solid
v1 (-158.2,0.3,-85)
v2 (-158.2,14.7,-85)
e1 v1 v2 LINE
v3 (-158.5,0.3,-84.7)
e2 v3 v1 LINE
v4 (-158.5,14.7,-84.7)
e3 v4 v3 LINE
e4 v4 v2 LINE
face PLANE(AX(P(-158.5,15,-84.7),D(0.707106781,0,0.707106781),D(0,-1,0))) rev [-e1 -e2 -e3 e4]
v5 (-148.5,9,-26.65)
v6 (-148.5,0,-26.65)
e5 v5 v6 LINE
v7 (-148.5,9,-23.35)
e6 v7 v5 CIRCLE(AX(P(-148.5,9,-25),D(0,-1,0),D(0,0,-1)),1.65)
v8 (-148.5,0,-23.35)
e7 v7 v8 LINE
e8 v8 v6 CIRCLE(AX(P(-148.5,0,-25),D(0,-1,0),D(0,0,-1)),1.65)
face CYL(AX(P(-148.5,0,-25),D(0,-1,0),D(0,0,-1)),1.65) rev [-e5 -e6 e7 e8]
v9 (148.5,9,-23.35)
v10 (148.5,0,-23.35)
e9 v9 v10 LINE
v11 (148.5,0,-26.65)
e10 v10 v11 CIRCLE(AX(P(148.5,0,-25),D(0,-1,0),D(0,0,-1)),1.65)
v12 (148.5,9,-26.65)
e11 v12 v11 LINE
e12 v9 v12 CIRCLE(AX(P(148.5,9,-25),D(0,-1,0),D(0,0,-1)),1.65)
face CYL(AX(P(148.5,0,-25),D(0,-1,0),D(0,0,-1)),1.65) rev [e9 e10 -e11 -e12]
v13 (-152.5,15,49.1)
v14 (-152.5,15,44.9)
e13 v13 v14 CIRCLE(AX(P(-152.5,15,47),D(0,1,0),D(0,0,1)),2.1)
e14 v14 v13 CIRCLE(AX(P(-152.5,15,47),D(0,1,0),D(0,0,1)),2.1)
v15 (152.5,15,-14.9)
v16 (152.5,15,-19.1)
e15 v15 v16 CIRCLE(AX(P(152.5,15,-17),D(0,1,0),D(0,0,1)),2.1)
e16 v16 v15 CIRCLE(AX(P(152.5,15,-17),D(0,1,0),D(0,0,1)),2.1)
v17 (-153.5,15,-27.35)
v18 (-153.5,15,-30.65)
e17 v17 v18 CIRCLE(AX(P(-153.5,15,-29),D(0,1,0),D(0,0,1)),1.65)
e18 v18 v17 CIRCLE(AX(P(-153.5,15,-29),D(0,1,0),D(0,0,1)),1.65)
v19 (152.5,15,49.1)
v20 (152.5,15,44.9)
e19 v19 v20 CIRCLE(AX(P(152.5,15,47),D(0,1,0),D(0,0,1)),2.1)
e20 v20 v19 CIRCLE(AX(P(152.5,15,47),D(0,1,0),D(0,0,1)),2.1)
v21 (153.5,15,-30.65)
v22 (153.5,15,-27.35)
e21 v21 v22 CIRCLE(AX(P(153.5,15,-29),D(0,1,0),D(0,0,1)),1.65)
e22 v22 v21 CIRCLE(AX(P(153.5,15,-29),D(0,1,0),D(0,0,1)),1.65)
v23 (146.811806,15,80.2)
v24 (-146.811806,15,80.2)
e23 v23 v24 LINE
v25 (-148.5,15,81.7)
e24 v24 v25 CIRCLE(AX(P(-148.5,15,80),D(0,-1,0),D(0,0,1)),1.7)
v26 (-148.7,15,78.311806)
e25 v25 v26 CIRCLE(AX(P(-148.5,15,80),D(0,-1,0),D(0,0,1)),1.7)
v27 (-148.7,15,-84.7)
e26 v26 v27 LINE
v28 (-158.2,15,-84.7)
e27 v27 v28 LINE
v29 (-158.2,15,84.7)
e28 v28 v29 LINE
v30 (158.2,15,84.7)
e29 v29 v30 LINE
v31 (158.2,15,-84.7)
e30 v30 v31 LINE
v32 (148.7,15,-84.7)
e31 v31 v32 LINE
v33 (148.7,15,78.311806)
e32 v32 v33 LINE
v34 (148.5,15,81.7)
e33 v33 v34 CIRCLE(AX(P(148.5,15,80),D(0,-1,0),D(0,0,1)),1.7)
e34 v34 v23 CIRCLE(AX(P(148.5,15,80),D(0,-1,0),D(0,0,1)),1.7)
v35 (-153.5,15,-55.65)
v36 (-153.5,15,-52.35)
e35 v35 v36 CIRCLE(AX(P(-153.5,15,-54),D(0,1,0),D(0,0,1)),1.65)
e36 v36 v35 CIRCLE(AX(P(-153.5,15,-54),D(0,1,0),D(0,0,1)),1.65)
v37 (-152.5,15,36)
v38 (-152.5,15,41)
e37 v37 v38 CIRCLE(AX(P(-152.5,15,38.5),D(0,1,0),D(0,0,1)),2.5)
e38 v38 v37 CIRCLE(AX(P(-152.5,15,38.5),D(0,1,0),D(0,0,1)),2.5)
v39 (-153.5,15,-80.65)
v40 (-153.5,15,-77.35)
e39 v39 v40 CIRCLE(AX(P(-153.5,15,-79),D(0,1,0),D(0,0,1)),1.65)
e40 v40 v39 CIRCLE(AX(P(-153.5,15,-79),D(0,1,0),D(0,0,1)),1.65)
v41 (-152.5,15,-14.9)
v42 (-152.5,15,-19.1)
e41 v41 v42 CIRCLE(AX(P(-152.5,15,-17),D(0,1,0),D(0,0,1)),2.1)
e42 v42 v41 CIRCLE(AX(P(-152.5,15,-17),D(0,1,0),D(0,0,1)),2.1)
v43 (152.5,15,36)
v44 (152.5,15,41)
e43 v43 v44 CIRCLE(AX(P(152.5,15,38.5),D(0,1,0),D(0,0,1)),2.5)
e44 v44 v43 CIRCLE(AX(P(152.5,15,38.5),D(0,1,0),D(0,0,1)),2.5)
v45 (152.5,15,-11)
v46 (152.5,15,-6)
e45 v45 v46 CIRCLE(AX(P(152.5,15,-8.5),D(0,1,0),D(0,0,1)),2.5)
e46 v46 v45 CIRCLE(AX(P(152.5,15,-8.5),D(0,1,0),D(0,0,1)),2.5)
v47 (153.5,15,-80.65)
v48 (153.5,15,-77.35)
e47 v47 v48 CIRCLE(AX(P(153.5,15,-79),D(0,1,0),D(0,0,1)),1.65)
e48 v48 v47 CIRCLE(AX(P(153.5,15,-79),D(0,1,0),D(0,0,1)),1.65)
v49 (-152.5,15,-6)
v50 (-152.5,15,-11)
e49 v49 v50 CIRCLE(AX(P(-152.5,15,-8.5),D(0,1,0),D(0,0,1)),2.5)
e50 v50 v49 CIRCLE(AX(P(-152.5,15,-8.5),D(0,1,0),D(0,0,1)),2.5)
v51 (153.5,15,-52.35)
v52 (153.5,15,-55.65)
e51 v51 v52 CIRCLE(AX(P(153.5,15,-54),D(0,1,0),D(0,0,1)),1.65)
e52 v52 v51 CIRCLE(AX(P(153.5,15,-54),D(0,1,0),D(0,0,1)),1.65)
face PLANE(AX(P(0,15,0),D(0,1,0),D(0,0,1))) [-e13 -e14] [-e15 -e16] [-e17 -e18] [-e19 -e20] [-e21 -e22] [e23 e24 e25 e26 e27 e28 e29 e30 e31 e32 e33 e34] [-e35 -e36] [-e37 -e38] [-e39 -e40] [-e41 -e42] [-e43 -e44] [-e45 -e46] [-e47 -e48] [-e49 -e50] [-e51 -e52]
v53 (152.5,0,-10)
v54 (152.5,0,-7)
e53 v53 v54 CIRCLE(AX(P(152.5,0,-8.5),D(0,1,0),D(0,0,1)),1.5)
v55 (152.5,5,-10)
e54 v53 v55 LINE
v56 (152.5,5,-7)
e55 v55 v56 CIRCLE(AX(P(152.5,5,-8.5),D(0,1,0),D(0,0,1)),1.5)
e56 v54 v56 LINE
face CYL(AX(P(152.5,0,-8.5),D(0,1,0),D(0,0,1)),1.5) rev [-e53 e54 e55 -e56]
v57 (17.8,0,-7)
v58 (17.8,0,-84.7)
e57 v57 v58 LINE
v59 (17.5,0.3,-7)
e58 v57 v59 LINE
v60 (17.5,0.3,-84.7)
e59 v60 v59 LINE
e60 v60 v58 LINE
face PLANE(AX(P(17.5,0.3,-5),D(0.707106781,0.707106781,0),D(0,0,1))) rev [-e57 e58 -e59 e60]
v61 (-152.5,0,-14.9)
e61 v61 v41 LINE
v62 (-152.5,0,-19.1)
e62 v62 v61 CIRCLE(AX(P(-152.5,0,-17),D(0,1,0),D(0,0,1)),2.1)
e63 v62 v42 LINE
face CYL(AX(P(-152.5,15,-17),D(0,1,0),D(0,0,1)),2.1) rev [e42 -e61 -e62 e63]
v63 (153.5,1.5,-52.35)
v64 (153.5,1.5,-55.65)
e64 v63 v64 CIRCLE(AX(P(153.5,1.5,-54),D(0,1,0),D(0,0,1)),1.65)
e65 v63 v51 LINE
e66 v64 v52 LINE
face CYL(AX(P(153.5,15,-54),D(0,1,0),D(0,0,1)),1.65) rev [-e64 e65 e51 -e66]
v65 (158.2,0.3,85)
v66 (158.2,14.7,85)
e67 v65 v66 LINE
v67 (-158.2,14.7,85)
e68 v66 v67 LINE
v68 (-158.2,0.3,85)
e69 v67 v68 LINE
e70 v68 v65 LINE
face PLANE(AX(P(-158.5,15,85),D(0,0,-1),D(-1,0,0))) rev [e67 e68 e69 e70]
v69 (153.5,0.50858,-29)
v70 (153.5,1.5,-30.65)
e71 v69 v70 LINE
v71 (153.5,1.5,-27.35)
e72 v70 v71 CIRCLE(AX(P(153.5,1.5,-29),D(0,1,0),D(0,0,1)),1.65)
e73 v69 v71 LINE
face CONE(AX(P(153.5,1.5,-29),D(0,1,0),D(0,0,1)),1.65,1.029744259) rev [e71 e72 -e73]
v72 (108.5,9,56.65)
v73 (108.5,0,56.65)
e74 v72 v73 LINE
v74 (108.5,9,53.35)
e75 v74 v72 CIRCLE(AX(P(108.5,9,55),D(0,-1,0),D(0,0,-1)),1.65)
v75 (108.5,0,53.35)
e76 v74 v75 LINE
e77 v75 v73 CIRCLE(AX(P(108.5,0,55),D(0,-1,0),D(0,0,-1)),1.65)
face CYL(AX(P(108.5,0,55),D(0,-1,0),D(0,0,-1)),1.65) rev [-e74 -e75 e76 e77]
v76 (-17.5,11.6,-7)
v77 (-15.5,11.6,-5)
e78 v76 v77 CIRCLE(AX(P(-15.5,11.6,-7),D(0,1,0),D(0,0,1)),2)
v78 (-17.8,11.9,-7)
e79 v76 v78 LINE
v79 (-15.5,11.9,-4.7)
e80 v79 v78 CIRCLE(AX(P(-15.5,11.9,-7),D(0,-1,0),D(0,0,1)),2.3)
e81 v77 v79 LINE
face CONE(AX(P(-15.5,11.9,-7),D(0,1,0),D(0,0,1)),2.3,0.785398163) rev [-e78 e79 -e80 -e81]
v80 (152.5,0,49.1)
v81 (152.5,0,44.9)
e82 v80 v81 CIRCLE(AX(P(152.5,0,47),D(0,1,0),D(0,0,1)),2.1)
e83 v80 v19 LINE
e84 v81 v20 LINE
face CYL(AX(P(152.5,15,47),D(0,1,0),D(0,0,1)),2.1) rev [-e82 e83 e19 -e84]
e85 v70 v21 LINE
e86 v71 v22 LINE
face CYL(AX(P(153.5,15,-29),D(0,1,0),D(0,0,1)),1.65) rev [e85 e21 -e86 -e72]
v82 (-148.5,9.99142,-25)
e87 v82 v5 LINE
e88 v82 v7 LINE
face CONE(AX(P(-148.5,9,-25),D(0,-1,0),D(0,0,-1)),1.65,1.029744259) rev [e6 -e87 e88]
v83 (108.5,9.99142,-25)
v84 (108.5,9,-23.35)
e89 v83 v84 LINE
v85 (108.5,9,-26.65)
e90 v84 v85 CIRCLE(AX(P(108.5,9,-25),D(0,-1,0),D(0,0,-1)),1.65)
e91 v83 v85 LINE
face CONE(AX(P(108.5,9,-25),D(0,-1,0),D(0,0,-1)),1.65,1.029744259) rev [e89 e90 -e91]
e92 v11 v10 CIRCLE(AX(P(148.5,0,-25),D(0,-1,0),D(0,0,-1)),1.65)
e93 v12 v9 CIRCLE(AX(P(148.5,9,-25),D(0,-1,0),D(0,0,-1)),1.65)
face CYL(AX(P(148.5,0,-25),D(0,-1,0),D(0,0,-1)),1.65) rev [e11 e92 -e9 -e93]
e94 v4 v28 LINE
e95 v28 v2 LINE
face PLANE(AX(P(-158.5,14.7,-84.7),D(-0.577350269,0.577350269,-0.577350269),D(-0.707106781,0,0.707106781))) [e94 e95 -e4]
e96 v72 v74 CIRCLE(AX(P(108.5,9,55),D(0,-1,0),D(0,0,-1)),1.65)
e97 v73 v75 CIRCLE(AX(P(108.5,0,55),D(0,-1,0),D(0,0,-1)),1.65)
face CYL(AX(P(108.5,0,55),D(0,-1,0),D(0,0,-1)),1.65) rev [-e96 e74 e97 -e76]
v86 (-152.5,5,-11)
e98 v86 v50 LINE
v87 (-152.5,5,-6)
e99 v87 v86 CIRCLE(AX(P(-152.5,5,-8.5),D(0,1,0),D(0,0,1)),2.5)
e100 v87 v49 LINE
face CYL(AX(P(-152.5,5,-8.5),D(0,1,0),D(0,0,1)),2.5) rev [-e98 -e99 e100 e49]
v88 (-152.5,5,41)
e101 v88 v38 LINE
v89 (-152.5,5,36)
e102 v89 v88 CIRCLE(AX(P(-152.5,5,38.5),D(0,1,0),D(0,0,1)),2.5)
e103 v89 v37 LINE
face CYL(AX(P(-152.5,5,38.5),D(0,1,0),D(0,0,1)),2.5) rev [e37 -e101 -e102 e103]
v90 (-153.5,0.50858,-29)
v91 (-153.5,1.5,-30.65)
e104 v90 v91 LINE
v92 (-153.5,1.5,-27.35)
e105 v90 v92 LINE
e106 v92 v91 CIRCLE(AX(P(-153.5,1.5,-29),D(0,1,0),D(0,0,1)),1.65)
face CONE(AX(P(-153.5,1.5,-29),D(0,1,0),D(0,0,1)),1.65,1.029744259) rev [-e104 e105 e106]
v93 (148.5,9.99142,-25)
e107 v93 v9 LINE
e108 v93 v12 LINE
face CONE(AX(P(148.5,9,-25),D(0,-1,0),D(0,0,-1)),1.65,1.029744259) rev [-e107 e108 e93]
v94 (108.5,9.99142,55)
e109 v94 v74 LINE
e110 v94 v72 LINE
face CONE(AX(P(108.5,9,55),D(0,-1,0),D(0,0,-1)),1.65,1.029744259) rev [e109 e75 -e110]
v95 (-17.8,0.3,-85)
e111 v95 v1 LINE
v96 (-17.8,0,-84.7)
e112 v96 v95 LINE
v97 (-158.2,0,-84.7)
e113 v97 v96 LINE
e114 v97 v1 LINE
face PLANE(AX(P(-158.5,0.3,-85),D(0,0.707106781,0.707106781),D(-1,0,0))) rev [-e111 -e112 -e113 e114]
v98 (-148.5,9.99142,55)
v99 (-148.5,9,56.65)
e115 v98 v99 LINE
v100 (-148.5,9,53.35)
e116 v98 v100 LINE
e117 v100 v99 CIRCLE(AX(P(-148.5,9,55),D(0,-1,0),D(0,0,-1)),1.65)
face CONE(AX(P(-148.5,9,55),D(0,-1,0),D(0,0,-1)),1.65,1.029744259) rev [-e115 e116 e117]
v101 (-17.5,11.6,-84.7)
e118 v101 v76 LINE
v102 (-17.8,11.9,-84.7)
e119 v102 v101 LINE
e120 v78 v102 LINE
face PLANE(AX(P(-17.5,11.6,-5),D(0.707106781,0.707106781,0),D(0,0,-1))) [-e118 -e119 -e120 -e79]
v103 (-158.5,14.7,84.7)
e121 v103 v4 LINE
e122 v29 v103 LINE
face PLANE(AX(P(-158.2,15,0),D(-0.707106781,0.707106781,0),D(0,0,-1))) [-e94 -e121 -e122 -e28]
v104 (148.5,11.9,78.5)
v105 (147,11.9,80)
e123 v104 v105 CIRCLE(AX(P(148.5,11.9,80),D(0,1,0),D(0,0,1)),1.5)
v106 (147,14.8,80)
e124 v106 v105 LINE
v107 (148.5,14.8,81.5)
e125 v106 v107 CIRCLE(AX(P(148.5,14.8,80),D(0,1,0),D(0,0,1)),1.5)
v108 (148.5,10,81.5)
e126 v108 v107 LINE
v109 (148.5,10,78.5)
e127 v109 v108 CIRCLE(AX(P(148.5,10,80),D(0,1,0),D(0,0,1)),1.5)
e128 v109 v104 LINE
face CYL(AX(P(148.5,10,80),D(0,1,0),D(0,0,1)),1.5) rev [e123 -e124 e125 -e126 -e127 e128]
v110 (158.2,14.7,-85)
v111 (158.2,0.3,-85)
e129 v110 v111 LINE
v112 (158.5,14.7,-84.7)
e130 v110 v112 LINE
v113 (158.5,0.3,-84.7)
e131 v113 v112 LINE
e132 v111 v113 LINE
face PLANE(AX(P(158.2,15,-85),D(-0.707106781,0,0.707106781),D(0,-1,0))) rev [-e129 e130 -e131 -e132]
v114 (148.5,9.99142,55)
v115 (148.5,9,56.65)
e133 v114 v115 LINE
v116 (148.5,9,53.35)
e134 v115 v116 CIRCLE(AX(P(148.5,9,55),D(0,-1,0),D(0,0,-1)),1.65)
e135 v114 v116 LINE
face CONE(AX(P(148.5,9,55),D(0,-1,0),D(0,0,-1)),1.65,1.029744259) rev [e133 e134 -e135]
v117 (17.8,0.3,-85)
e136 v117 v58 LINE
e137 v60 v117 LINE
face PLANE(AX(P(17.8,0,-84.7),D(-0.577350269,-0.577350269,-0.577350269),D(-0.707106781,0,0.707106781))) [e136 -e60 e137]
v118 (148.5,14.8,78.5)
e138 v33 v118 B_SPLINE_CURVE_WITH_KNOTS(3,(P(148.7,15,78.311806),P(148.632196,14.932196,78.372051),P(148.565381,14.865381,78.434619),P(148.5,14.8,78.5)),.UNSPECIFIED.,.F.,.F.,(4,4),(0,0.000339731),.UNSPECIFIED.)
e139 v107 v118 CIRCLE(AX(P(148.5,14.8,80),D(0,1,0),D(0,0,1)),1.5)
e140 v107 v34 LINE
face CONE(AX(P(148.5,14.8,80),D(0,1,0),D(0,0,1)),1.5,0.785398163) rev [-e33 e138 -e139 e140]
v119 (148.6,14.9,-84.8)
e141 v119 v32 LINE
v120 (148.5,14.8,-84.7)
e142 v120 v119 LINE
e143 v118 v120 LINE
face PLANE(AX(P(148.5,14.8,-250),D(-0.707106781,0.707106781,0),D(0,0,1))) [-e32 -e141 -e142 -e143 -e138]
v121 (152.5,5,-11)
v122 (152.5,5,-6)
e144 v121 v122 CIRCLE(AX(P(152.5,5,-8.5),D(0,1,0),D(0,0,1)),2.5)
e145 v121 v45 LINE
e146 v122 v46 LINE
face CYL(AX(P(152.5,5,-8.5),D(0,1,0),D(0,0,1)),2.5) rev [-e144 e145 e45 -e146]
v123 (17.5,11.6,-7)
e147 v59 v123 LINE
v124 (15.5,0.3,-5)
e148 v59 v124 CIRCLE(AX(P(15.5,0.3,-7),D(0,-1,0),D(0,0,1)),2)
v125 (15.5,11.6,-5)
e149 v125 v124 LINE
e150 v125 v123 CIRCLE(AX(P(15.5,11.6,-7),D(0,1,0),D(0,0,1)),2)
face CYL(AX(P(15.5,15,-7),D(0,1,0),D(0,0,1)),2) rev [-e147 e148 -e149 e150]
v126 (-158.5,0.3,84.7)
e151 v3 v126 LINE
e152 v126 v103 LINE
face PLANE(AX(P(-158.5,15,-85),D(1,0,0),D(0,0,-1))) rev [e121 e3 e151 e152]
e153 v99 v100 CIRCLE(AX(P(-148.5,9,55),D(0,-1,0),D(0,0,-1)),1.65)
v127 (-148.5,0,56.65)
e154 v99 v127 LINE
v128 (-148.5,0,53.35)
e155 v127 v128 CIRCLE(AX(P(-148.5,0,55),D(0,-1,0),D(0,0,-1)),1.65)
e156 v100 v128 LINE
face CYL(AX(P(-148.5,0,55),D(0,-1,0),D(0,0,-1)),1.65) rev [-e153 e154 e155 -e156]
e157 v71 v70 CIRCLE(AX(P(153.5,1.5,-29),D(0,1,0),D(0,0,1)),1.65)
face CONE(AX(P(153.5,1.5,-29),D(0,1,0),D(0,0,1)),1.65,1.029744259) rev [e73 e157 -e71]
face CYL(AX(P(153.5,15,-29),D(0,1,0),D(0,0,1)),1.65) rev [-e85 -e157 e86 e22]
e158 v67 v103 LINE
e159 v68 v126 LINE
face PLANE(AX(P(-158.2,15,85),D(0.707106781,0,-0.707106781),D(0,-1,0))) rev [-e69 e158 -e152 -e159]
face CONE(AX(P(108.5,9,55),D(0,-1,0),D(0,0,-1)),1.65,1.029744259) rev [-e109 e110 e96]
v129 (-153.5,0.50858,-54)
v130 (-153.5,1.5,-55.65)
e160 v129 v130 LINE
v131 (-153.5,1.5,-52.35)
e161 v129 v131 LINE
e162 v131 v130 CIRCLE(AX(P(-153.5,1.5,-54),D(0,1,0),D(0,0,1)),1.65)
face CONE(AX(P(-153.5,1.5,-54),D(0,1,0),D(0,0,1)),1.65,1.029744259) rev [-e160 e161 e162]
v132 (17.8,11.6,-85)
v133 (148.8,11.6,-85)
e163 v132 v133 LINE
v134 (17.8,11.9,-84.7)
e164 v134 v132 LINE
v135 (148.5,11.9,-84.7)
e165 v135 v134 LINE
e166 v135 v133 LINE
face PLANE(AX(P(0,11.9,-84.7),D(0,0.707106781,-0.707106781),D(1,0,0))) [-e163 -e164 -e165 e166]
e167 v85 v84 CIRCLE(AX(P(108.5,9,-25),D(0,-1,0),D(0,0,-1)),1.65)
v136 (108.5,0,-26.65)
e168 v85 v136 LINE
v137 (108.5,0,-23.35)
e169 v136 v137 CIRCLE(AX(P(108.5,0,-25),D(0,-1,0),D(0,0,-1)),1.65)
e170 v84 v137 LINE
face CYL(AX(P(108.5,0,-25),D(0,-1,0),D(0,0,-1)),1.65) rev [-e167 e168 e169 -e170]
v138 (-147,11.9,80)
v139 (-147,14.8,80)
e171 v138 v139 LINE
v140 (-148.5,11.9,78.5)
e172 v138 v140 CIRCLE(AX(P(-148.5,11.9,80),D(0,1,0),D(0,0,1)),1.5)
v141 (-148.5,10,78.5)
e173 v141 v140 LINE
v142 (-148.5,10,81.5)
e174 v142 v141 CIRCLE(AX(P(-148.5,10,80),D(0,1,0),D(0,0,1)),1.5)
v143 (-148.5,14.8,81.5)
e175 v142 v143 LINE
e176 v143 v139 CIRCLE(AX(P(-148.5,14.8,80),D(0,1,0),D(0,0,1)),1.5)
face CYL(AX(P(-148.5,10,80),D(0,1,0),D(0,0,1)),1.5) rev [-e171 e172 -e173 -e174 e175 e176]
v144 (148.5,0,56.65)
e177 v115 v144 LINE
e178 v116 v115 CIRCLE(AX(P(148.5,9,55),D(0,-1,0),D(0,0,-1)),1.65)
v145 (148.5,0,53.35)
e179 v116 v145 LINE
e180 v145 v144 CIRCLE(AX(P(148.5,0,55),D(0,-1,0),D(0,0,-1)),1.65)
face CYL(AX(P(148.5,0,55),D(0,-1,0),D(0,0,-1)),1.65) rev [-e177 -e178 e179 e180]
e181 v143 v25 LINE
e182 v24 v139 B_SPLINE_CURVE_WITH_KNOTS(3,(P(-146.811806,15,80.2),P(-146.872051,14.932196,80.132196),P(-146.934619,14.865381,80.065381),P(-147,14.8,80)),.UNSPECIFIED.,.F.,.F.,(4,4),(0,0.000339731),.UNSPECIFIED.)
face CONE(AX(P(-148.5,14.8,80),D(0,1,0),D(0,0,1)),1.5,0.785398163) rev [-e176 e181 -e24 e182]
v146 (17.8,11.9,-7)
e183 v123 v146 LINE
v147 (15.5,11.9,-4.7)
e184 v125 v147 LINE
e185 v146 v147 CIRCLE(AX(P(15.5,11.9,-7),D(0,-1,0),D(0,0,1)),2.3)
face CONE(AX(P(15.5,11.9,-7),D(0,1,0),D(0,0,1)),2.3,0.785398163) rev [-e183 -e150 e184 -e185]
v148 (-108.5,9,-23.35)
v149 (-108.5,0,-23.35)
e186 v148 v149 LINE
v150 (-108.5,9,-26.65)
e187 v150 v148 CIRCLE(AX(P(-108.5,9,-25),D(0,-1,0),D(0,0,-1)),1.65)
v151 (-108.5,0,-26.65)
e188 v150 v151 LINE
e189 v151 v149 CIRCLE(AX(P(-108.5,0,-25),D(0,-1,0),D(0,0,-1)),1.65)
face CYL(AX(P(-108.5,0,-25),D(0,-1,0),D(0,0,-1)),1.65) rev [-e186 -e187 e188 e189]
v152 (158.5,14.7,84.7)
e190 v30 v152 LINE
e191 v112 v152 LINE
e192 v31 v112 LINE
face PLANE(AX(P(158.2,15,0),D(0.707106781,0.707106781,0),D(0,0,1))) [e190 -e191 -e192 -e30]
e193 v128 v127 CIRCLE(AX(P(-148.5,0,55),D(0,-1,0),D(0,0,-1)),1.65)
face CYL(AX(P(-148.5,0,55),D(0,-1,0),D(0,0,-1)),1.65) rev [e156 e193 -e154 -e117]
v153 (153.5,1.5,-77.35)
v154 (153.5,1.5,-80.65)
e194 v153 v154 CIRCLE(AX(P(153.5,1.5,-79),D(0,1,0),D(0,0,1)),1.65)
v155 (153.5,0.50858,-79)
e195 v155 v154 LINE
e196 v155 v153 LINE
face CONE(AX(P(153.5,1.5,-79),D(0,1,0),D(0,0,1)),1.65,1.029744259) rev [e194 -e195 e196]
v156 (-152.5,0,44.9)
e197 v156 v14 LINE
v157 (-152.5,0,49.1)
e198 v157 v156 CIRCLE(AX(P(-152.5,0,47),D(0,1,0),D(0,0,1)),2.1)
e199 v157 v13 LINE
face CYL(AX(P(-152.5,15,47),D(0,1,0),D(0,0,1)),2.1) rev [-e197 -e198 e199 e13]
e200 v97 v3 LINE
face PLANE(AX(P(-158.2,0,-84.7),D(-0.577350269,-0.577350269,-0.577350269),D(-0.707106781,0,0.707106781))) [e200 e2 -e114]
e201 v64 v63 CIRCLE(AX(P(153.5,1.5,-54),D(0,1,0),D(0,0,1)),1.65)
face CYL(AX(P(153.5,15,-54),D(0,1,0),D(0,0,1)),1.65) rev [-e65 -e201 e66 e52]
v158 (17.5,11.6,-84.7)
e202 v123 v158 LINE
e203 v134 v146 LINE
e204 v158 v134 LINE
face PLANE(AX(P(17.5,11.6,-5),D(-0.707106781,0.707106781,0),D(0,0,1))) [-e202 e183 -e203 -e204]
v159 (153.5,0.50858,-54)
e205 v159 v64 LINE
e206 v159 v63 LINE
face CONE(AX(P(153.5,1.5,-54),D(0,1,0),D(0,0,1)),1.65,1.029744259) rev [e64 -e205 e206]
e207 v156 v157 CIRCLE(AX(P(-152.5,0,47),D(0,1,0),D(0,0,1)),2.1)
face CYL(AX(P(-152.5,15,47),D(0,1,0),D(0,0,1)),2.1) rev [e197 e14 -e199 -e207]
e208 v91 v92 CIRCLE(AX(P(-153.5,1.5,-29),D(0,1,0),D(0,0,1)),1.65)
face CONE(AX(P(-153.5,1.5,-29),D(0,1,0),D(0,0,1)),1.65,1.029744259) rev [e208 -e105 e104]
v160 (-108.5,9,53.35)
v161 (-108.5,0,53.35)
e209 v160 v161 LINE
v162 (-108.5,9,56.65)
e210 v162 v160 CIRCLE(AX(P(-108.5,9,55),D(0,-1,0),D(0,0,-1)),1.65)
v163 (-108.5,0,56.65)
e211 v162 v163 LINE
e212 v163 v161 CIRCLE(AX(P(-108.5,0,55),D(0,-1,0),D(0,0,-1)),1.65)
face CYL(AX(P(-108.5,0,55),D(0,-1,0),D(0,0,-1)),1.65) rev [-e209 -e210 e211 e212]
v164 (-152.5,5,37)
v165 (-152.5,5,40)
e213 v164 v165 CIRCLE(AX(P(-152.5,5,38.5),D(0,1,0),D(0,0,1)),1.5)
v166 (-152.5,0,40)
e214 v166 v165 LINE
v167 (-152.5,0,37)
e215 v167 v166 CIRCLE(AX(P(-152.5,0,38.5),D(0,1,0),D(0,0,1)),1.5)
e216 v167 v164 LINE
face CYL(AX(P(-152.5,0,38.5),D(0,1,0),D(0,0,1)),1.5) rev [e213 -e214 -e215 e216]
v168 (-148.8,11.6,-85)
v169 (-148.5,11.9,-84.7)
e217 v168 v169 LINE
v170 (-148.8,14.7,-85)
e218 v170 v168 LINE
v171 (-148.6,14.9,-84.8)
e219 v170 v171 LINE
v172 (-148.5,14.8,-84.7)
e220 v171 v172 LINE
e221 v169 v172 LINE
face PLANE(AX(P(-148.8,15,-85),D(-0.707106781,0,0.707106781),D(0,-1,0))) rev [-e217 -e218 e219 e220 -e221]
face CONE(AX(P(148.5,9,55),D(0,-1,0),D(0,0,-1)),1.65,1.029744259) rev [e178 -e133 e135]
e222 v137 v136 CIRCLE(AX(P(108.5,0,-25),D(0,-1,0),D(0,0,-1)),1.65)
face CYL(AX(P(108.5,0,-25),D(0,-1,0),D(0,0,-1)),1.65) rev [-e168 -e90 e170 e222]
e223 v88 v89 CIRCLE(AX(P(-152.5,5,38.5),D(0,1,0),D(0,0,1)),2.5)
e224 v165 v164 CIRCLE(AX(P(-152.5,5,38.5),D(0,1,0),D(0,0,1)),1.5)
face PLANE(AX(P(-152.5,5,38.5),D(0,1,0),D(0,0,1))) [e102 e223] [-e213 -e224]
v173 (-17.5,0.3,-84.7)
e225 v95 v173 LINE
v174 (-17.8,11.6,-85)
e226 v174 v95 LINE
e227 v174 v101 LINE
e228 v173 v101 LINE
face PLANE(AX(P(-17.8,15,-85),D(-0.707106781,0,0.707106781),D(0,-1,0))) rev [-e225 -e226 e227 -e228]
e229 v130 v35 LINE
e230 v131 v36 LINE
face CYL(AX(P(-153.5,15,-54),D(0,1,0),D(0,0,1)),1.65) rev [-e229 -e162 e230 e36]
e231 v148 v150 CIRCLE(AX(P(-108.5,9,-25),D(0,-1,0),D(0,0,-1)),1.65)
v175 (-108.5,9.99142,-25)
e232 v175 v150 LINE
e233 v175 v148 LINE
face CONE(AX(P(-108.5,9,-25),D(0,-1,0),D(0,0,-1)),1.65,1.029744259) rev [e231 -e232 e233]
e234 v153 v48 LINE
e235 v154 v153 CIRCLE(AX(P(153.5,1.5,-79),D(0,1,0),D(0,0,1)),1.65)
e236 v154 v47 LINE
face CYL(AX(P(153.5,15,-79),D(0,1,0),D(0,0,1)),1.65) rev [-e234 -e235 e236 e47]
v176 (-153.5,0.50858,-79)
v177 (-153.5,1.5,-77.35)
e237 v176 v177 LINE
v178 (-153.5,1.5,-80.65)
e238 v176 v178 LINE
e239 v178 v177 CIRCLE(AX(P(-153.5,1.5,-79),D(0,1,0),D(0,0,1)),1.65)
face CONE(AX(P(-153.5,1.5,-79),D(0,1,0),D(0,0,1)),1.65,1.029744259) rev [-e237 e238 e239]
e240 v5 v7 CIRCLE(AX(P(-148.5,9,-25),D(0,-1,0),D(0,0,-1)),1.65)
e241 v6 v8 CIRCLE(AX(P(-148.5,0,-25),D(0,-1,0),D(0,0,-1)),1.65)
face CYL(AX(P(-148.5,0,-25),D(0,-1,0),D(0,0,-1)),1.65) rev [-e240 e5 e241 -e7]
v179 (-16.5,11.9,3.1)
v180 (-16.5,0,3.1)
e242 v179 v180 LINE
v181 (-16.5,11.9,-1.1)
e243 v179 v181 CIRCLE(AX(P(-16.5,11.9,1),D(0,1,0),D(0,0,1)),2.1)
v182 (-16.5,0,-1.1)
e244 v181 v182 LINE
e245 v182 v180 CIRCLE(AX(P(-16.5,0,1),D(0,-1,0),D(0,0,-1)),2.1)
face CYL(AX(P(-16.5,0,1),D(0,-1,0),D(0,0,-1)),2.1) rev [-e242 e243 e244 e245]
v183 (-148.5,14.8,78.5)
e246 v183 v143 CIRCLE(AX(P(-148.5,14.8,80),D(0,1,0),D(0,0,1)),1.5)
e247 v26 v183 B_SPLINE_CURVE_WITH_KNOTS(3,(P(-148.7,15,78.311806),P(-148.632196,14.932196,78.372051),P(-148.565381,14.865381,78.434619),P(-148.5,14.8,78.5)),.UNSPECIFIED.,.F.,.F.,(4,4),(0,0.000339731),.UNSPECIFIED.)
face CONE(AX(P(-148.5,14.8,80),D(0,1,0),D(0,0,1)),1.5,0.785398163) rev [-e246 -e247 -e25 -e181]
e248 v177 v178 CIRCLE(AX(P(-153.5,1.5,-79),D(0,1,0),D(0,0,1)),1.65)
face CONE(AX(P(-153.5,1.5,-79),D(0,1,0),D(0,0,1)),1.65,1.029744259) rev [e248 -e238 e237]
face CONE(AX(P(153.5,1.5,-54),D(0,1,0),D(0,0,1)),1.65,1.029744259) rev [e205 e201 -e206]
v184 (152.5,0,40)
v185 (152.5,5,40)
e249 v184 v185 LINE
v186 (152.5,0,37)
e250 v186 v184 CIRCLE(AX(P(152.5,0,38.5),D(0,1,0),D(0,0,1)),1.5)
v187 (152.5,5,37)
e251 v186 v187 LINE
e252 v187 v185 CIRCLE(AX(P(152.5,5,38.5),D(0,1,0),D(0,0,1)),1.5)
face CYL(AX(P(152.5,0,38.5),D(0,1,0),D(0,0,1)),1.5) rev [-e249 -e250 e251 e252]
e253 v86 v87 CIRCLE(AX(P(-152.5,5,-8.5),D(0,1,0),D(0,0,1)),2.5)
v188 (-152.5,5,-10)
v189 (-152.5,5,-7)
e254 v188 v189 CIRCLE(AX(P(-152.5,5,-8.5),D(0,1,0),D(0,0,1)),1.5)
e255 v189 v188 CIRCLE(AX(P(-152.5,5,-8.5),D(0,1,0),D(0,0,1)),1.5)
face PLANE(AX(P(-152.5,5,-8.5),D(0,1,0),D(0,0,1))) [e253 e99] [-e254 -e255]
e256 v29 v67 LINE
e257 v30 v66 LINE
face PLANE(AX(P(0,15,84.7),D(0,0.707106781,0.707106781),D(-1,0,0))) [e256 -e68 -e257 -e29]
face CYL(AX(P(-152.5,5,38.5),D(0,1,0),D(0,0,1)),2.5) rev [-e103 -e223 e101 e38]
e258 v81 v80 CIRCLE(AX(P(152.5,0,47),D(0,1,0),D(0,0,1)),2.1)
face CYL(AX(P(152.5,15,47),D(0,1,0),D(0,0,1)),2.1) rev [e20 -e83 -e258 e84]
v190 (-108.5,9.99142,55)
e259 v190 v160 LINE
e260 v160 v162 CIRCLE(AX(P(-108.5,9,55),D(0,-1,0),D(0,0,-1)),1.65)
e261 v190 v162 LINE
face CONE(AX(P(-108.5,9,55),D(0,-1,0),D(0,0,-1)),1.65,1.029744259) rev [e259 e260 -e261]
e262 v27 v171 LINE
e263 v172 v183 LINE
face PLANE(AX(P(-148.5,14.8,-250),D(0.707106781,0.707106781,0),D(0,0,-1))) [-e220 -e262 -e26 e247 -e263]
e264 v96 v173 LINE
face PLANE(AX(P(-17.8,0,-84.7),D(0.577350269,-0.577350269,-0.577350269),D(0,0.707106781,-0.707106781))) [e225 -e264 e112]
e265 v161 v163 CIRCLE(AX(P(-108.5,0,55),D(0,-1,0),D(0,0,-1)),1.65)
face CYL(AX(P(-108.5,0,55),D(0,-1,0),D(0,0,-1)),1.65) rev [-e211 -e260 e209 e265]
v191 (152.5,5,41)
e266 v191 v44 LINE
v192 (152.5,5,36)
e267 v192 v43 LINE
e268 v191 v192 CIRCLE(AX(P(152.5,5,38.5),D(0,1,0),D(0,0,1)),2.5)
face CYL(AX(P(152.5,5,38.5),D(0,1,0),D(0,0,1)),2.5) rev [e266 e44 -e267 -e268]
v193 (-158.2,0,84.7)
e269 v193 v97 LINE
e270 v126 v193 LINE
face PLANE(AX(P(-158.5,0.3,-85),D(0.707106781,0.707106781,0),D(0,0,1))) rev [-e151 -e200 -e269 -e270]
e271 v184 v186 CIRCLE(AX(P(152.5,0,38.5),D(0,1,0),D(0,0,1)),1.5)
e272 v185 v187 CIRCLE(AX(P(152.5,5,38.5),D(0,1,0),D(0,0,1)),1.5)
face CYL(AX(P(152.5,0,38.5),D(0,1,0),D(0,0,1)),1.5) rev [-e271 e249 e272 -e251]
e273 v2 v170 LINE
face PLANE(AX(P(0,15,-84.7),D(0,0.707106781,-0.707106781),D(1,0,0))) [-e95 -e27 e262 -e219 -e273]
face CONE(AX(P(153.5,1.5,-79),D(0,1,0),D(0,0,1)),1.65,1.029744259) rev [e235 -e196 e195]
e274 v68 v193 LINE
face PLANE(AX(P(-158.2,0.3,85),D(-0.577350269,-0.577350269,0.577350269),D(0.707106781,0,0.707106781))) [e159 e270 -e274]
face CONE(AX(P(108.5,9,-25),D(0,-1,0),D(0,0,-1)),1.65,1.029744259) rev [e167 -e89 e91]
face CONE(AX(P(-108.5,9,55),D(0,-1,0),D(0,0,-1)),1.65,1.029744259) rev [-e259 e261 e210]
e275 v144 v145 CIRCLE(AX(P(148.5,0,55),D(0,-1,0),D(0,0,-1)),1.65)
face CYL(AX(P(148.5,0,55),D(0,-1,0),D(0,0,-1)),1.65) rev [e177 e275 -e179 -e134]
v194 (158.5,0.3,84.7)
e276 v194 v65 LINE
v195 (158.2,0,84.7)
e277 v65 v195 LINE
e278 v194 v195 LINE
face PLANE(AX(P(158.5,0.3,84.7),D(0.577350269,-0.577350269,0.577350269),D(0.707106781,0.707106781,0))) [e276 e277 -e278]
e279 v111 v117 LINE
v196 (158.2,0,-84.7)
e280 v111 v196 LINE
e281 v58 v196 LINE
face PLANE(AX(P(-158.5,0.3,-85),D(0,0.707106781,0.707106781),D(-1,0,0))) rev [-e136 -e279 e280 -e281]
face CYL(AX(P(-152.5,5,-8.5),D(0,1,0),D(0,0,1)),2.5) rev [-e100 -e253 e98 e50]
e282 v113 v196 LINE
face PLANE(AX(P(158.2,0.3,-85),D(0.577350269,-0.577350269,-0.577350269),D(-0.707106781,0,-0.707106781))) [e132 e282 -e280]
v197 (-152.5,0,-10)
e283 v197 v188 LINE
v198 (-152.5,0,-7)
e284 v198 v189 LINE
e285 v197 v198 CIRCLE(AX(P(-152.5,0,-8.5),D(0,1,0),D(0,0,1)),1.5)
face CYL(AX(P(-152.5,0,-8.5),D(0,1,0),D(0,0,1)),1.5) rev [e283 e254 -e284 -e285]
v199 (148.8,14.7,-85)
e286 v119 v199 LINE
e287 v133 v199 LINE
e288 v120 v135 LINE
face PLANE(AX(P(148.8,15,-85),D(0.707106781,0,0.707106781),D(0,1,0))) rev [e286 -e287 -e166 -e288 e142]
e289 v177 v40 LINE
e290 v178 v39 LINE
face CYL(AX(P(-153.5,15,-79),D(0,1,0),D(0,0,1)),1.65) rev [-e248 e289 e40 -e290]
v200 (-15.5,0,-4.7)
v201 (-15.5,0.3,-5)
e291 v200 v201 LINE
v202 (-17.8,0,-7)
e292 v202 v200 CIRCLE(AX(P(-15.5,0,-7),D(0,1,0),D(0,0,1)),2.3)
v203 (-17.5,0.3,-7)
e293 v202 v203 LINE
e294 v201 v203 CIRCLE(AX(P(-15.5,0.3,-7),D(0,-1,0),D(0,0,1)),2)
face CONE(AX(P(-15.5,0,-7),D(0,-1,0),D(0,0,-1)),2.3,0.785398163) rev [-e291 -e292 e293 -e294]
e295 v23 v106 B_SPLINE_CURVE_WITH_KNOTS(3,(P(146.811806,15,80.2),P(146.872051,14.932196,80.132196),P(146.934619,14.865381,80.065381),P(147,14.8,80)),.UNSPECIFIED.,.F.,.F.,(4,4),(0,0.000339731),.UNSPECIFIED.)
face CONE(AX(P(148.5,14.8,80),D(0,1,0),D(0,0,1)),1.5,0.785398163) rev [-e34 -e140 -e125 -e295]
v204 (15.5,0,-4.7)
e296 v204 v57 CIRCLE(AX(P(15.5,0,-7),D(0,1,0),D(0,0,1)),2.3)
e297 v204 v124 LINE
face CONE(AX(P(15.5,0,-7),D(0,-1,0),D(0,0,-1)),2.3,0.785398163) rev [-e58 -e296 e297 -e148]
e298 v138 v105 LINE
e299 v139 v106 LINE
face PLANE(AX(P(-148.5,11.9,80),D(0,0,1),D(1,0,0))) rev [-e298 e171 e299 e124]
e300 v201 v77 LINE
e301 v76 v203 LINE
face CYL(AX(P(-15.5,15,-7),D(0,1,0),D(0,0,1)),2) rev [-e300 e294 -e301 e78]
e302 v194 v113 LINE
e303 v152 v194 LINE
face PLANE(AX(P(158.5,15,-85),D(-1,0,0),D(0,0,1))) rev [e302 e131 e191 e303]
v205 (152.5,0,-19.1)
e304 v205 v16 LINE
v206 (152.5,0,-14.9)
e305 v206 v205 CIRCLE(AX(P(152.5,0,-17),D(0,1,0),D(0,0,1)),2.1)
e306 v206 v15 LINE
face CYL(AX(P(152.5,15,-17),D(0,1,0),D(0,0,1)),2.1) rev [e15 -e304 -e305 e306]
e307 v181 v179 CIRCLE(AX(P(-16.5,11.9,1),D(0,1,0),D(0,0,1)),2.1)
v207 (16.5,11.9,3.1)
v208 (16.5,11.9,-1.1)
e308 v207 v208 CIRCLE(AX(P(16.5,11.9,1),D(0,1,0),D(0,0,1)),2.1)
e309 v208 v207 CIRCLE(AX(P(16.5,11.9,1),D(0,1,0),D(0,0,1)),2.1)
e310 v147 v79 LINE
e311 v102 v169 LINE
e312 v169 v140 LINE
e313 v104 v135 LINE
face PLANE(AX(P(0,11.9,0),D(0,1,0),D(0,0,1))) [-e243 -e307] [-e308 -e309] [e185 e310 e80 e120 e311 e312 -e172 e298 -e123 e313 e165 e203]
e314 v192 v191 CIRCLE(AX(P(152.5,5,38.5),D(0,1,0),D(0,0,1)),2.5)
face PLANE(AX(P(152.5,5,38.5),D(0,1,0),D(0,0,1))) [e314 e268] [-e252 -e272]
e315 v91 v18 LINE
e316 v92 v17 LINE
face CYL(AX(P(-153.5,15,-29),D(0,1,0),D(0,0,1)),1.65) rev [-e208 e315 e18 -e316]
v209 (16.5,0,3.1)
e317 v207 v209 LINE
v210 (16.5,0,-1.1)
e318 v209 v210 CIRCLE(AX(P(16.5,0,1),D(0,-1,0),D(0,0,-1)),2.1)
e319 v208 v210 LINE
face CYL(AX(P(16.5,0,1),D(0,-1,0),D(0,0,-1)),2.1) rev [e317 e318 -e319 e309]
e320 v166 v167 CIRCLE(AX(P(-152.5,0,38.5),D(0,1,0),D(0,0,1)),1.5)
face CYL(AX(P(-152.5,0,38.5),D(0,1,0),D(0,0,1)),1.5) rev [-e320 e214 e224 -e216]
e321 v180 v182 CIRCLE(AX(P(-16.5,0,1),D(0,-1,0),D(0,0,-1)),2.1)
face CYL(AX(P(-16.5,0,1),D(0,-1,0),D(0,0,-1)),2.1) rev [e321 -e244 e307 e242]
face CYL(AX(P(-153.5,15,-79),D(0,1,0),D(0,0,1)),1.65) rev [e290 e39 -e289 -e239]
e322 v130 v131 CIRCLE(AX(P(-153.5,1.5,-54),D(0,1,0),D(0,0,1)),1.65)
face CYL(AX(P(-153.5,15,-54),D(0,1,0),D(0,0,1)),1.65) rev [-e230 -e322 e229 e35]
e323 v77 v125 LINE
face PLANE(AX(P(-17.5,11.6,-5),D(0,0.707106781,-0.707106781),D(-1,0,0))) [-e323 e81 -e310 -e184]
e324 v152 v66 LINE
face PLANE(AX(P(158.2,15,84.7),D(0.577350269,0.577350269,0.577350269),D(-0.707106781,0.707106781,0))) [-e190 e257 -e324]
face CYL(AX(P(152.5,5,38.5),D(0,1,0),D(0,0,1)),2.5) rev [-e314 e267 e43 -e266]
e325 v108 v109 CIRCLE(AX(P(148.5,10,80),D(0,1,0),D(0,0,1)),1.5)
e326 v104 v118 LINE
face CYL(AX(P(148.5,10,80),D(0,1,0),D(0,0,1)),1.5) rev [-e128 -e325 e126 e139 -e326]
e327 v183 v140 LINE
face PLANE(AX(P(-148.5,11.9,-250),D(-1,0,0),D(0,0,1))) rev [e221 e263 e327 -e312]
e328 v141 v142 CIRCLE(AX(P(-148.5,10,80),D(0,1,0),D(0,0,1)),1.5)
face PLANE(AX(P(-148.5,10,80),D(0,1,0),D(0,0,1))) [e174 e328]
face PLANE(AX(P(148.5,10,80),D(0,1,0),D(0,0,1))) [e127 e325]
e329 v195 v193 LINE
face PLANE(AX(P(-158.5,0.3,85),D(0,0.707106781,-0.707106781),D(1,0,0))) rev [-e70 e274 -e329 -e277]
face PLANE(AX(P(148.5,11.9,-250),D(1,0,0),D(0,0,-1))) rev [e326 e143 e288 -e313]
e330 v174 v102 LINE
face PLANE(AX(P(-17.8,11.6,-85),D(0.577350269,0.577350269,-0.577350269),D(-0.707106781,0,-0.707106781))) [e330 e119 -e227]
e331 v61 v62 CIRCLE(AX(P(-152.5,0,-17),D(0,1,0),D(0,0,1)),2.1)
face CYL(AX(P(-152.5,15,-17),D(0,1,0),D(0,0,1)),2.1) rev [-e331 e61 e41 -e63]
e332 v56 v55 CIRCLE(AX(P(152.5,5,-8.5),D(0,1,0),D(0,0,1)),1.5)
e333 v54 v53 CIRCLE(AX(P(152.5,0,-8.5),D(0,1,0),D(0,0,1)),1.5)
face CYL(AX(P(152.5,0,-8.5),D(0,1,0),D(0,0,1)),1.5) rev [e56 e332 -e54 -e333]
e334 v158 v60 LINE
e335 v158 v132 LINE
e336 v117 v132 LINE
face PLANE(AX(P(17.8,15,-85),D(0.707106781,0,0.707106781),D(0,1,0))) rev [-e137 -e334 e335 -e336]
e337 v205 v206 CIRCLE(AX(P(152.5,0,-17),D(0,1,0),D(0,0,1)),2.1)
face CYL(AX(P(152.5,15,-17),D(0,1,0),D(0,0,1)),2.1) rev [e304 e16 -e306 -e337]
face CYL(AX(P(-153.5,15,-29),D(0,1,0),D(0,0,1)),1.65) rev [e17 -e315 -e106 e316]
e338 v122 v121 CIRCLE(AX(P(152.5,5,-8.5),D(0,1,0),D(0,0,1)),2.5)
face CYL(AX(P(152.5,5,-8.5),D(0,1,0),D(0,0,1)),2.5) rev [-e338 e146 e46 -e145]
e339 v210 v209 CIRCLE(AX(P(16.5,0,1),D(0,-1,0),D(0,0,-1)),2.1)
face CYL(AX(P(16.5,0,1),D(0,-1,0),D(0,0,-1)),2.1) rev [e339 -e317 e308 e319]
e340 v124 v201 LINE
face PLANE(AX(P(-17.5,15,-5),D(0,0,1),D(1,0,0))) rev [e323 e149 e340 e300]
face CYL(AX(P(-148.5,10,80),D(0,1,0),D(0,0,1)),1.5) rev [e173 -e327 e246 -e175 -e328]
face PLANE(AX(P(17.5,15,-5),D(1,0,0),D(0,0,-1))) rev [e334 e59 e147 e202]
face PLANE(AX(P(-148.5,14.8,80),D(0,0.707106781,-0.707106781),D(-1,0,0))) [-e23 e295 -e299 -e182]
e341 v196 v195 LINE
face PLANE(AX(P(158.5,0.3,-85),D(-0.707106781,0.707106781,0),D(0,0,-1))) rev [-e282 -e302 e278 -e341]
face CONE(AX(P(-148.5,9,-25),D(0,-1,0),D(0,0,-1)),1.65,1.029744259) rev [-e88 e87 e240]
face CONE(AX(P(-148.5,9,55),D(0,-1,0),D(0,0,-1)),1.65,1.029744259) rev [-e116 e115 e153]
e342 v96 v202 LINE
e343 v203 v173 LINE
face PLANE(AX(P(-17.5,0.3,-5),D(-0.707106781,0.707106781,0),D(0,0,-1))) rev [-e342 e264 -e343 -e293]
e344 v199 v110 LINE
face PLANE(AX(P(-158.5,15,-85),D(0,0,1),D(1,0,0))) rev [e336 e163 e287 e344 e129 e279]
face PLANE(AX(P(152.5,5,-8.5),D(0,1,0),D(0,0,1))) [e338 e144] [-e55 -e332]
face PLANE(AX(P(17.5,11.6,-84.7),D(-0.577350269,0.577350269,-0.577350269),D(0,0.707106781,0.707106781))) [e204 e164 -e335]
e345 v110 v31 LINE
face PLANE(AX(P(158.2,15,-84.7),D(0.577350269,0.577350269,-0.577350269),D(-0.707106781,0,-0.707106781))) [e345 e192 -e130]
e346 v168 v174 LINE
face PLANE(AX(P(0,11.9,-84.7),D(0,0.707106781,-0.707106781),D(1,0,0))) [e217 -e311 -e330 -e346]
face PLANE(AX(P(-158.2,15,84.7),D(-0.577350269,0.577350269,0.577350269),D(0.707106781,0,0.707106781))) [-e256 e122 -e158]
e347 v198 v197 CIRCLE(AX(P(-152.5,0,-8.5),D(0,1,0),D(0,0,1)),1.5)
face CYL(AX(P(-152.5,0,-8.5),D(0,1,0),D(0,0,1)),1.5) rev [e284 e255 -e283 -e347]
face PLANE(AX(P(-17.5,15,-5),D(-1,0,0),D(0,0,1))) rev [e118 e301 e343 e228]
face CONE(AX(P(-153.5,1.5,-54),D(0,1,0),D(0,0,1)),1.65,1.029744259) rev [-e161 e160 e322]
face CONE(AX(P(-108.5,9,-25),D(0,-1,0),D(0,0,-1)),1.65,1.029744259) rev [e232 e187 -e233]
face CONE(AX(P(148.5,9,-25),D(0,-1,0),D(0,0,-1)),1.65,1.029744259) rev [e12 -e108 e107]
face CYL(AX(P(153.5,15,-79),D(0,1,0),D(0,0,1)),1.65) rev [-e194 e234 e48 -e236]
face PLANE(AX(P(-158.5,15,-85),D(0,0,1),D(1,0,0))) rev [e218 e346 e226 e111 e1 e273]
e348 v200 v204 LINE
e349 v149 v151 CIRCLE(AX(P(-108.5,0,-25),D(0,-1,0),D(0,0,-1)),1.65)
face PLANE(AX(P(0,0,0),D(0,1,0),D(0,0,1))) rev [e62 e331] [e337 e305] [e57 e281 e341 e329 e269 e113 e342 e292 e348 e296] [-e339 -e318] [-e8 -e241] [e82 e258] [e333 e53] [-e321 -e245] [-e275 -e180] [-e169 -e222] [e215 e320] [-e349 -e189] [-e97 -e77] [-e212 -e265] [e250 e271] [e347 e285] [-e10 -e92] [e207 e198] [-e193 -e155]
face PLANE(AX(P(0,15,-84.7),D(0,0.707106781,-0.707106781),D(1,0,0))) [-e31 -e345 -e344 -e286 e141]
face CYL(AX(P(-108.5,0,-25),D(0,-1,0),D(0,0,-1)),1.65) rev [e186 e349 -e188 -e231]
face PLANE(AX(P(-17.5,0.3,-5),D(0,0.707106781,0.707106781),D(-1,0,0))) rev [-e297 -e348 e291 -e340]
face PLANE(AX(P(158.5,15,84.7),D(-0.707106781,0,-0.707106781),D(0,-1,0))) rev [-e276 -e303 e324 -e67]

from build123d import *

# Parameters (mm, degrees)
SKETCH_1_W             = 317
SKETCH_1_H             = 170
EXTRUDE_1_DEPTH        = 15
SKETCH_2_W             = 297
SKETCH_2_H             = 330
CUT_EXTRUDE_1_DEPTH    = 3.1
SKETCH_3_W             = 35
SKETCH_3_H             = 103.554222687
CUT_EXTRUDE_2_DEPTH    = 181.477837975
HOLE_WIZARD_M5_1_D     = 4.2
HOLE_WIZARD_M5_1_DEPTH = 16
HOLE_WIZARD_M5_1_TIP   = 1.2618073
FILLET_1_R             = 2
SKETCH_6_R             = 1.5
CUT_EXTRUDE_3_DEPTH    = 5
CHAMFER_1_SIZE         = 0.3
HOLE_WIZARD_M5_2_D     = 4.2
HOLE_WIZARD_M4_1_D     = 3.3
HOLE_WIZARD_M4_1_DEPTH = 13.5
HOLE_WIZARD_M4_1_TIP   = 0.991420021
SKETCH_11_R            = 2.5
CUT_EXTRUDE_4_DEPTH    = 10
SKETCH_12_R            = 1.5
CUT_EXTRUDE_5_DEPTH    = 181.477837975
HOLE_WIZARD_M4_2_D     = 3.3
HOLE_WIZARD_M4_2_DEPTH = 9
HOLE_WIZARD_M4_2_TIP   = 0.991420021
CHAMFER_3_SIZE         = 0.2


with BuildPart() as part:
    # 草图1 → 凸台-拉伸1 (new body)
    with BuildSketch(Plane(origin=(0, 0, 0), x_dir=(1, 0, 0), z_dir=(0, 1, 0))):
        Rectangle(SKETCH_1_W, SKETCH_1_H)
    extrude(amount=EXTRUDE_1_DEPTH)

    # 草图2 → 切除-拉伸1 (cut)
    with BuildSketch(Plane(origin=(0, 15, 0), x_dir=(1, 0, 0), z_dir=(0, 1, 0))):
        with Locations((0, 85)):
            Rectangle(SKETCH_2_W, SKETCH_2_H)
    extrude(amount=-CUT_EXTRUDE_1_DEPTH, mode=Mode.SUBTRACT)

    # 草图3 → 切除-拉伸2 (cut, through all)
    with BuildSketch(Plane.XZ):
        with Locations((0, -56.777111344)):
            Rectangle(SKETCH_3_W, SKETCH_3_H)
    extrude(amount=-CUT_EXTRUDE_2_DEPTH, mode=Mode.SUBTRACT)

    # M5 螺纹孔1
    with Locations(Plane(origin=(0, 0, 0), x_dir=(-1, 0, 0), z_dir=(0, -1, 0))):
        with Locations((-16.5, -1), (16.5, -1)):
            Hole(HOLE_WIZARD_M5_1_D / 2, depth=HOLE_WIZARD_M5_1_DEPTH)
            with Locations((0, 0, -(HOLE_WIZARD_M5_1_DEPTH + HOLE_WIZARD_M5_1_TIP / 2))):  # 118° drill point
                Cone(0, HOLE_WIZARD_M5_1_D / 2, HOLE_WIZARD_M5_1_TIP, mode=Mode.SUBTRACT)

    # 圆角1
    fillet_1_edges = [part.edges().sort_by_distance(p)[0] for p in [
        (17.5, 5.95, -5),
        (-17.5, 5.95, -5),
    ]]
    fillet(fillet_1_edges, radius=FILLET_1_R)

    # 草图6 → 切除-拉伸3 (cut)
    with BuildSketch(Plane(origin=(0, 15, 0), x_dir=(1, 0, 0), z_dir=(0, 1, 0))):
        with Locations(Location((-148.5, -80, 0), (0, 0, 270))):
            Circle(SKETCH_6_R)
        with Locations(Location((148.5, -80, 0), (0, 0, 270))):
            Circle(SKETCH_6_R)
    extrude(amount=-CUT_EXTRUDE_3_DEPTH, mode=Mode.SUBTRACT)

    # 倒角1
    chamfer_1_edges = [part.edges().sort_by_distance(p)[0] for p in [
        (-158.5, 15, 0),
        (0, 15, 85),
        (-153.5, 15, -85),
        (83, 11.9, -85),
        (148.5, 13.45, -85),
        (-148.5, 13.45, -85),
        (-83, 11.9, -85),
        (-17.5, 11.9, -46),
        (-88, 0, -85),
        (17.5, 0, -46),
        (17.5, 5.95, -85),
        (-17.5, 5.95, -85),
        (158.5, 15, 0),
        (0, 0, 85),
        (-158.5, 0, 0),
        (88, 0, -85),
        (158.5, 0, 0),
        (153.5, 15, -85),
        (0, 11.9, -5),
        (0, 0, -5),
        (158.5, 7.5, 85),
        (-158.5, 7.5, 85),
        (17.5, 11.9, -46),
        (-158.5, 7.5, -85),
        (-17.5, 0, -46),
        (158.5, 7.5, -85),
        (16.914213562, 0, -5.585786438),
        (16.914213562, 11.9, -5.585786438),
        (-16.914213562, 0, -5.585786438),
        (-16.914213562, 11.9, -5.585786438),
    ]]
    chamfer(chamfer_1_edges, length=CHAMFER_1_SIZE)

    # M5 螺纹孔2 (through all)
    with Locations(Plane(origin=(0, 15, 0), x_dir=(1, 0, 0), z_dir=(0, 1, 0))):
        with Locations((152.5, 17), (152.5, -47), (-152.5, 17), (-152.5, -47)):
            Hole(HOLE_WIZARD_M5_2_D / 2)

    # M4 螺纹孔1
    with Locations(Plane(origin=(0, 15, 0), x_dir=(1, 0, 0), z_dir=(0, 1, 0))):
        with Locations((153.5, 79), (153.5, 54), (153.5, 29), (-153.5, 29), (-153.5, 54), (-153.5, 79)):
            Hole(HOLE_WIZARD_M4_1_D / 2, depth=HOLE_WIZARD_M4_1_DEPTH)
            with Locations((0, 0, -(HOLE_WIZARD_M4_1_DEPTH + HOLE_WIZARD_M4_1_TIP / 2))):  # 118° drill point
                Cone(0, HOLE_WIZARD_M4_1_D / 2, HOLE_WIZARD_M4_1_TIP, mode=Mode.SUBTRACT)

    # 草图11 → 切除-拉伸4 (cut)
    with BuildSketch(Plane(origin=(0, 15, 0), x_dir=(1, 0, 0), z_dir=(0, 1, 0))):
        with Locations(Location((152.5, 8.5, 0), (0, 0, 270))):
            Circle(SKETCH_11_R)
        with Locations(Location((152.5, -38.5, 0), (0, 0, 270))):
            Circle(SKETCH_11_R)
        with Locations(Location((-152.5, 8.5, 0), (0, 0, 270))):
            Circle(SKETCH_11_R)
        with Locations(Location((-152.5, -38.5, 0), (0, 0, 270))):
            Circle(SKETCH_11_R)
    extrude(amount=-CUT_EXTRUDE_4_DEPTH, mode=Mode.SUBTRACT)

    # 草图12 → 切除-拉伸5 (cut, through all)
    with BuildSketch(Plane(origin=(0, 15, 0), x_dir=(1, 0, 0), z_dir=(0, 1, 0))):
        with Locations(Location((152.5, 8.5, 0), (0, 0, 270))):
            Circle(SKETCH_12_R)
        with Locations(Location((152.5, -38.5, 0), (0, 0, 270))):
            Circle(SKETCH_12_R)
        with Locations(Location((-152.5, 8.5, 0), (0, 0, 270))):
            Circle(SKETCH_12_R)
        with Locations(Location((-152.5, -38.5, 0), (0, 0, 270))):
            Circle(SKETCH_12_R)
    extrude(amount=-CUT_EXTRUDE_5_DEPTH, mode=Mode.SUBTRACT)

    # M4 螺纹孔2
    with Locations(Plane(origin=(0, 0, 0), x_dir=(-1, 0, 0), z_dir=(0, -1, 0))):
        with Locations((148.5, 25), (148.5, -55), (108.5, 25), (108.5, -55), (-148.5, 25), (-108.5, 25), (-148.5, -55), (-108.5, -55)):
            Hole(HOLE_WIZARD_M4_2_D / 2, depth=HOLE_WIZARD_M4_2_DEPTH)
            with Locations((0, 0, -(HOLE_WIZARD_M4_2_DEPTH + HOLE_WIZARD_M4_2_TIP / 2))):  # 118° drill point
                Cone(0, HOLE_WIZARD_M4_2_D / 2, HOLE_WIZARD_M4_2_TIP, mode=Mode.SUBTRACT)

    # 倒角3
    chamfer_3_edges = [part.edges().sort_by_distance(p)[0] for p in [
        (148.5, 15, -3.1),
        (150, 15, 80),
        (-148.5, 15, -3.1),
        (0, 15, 80),
        (-150, 15, 80),
    ]]
    chamfer(chamfer_3_edges, length=CHAMFER_3_SIZE)


solid = part.part
